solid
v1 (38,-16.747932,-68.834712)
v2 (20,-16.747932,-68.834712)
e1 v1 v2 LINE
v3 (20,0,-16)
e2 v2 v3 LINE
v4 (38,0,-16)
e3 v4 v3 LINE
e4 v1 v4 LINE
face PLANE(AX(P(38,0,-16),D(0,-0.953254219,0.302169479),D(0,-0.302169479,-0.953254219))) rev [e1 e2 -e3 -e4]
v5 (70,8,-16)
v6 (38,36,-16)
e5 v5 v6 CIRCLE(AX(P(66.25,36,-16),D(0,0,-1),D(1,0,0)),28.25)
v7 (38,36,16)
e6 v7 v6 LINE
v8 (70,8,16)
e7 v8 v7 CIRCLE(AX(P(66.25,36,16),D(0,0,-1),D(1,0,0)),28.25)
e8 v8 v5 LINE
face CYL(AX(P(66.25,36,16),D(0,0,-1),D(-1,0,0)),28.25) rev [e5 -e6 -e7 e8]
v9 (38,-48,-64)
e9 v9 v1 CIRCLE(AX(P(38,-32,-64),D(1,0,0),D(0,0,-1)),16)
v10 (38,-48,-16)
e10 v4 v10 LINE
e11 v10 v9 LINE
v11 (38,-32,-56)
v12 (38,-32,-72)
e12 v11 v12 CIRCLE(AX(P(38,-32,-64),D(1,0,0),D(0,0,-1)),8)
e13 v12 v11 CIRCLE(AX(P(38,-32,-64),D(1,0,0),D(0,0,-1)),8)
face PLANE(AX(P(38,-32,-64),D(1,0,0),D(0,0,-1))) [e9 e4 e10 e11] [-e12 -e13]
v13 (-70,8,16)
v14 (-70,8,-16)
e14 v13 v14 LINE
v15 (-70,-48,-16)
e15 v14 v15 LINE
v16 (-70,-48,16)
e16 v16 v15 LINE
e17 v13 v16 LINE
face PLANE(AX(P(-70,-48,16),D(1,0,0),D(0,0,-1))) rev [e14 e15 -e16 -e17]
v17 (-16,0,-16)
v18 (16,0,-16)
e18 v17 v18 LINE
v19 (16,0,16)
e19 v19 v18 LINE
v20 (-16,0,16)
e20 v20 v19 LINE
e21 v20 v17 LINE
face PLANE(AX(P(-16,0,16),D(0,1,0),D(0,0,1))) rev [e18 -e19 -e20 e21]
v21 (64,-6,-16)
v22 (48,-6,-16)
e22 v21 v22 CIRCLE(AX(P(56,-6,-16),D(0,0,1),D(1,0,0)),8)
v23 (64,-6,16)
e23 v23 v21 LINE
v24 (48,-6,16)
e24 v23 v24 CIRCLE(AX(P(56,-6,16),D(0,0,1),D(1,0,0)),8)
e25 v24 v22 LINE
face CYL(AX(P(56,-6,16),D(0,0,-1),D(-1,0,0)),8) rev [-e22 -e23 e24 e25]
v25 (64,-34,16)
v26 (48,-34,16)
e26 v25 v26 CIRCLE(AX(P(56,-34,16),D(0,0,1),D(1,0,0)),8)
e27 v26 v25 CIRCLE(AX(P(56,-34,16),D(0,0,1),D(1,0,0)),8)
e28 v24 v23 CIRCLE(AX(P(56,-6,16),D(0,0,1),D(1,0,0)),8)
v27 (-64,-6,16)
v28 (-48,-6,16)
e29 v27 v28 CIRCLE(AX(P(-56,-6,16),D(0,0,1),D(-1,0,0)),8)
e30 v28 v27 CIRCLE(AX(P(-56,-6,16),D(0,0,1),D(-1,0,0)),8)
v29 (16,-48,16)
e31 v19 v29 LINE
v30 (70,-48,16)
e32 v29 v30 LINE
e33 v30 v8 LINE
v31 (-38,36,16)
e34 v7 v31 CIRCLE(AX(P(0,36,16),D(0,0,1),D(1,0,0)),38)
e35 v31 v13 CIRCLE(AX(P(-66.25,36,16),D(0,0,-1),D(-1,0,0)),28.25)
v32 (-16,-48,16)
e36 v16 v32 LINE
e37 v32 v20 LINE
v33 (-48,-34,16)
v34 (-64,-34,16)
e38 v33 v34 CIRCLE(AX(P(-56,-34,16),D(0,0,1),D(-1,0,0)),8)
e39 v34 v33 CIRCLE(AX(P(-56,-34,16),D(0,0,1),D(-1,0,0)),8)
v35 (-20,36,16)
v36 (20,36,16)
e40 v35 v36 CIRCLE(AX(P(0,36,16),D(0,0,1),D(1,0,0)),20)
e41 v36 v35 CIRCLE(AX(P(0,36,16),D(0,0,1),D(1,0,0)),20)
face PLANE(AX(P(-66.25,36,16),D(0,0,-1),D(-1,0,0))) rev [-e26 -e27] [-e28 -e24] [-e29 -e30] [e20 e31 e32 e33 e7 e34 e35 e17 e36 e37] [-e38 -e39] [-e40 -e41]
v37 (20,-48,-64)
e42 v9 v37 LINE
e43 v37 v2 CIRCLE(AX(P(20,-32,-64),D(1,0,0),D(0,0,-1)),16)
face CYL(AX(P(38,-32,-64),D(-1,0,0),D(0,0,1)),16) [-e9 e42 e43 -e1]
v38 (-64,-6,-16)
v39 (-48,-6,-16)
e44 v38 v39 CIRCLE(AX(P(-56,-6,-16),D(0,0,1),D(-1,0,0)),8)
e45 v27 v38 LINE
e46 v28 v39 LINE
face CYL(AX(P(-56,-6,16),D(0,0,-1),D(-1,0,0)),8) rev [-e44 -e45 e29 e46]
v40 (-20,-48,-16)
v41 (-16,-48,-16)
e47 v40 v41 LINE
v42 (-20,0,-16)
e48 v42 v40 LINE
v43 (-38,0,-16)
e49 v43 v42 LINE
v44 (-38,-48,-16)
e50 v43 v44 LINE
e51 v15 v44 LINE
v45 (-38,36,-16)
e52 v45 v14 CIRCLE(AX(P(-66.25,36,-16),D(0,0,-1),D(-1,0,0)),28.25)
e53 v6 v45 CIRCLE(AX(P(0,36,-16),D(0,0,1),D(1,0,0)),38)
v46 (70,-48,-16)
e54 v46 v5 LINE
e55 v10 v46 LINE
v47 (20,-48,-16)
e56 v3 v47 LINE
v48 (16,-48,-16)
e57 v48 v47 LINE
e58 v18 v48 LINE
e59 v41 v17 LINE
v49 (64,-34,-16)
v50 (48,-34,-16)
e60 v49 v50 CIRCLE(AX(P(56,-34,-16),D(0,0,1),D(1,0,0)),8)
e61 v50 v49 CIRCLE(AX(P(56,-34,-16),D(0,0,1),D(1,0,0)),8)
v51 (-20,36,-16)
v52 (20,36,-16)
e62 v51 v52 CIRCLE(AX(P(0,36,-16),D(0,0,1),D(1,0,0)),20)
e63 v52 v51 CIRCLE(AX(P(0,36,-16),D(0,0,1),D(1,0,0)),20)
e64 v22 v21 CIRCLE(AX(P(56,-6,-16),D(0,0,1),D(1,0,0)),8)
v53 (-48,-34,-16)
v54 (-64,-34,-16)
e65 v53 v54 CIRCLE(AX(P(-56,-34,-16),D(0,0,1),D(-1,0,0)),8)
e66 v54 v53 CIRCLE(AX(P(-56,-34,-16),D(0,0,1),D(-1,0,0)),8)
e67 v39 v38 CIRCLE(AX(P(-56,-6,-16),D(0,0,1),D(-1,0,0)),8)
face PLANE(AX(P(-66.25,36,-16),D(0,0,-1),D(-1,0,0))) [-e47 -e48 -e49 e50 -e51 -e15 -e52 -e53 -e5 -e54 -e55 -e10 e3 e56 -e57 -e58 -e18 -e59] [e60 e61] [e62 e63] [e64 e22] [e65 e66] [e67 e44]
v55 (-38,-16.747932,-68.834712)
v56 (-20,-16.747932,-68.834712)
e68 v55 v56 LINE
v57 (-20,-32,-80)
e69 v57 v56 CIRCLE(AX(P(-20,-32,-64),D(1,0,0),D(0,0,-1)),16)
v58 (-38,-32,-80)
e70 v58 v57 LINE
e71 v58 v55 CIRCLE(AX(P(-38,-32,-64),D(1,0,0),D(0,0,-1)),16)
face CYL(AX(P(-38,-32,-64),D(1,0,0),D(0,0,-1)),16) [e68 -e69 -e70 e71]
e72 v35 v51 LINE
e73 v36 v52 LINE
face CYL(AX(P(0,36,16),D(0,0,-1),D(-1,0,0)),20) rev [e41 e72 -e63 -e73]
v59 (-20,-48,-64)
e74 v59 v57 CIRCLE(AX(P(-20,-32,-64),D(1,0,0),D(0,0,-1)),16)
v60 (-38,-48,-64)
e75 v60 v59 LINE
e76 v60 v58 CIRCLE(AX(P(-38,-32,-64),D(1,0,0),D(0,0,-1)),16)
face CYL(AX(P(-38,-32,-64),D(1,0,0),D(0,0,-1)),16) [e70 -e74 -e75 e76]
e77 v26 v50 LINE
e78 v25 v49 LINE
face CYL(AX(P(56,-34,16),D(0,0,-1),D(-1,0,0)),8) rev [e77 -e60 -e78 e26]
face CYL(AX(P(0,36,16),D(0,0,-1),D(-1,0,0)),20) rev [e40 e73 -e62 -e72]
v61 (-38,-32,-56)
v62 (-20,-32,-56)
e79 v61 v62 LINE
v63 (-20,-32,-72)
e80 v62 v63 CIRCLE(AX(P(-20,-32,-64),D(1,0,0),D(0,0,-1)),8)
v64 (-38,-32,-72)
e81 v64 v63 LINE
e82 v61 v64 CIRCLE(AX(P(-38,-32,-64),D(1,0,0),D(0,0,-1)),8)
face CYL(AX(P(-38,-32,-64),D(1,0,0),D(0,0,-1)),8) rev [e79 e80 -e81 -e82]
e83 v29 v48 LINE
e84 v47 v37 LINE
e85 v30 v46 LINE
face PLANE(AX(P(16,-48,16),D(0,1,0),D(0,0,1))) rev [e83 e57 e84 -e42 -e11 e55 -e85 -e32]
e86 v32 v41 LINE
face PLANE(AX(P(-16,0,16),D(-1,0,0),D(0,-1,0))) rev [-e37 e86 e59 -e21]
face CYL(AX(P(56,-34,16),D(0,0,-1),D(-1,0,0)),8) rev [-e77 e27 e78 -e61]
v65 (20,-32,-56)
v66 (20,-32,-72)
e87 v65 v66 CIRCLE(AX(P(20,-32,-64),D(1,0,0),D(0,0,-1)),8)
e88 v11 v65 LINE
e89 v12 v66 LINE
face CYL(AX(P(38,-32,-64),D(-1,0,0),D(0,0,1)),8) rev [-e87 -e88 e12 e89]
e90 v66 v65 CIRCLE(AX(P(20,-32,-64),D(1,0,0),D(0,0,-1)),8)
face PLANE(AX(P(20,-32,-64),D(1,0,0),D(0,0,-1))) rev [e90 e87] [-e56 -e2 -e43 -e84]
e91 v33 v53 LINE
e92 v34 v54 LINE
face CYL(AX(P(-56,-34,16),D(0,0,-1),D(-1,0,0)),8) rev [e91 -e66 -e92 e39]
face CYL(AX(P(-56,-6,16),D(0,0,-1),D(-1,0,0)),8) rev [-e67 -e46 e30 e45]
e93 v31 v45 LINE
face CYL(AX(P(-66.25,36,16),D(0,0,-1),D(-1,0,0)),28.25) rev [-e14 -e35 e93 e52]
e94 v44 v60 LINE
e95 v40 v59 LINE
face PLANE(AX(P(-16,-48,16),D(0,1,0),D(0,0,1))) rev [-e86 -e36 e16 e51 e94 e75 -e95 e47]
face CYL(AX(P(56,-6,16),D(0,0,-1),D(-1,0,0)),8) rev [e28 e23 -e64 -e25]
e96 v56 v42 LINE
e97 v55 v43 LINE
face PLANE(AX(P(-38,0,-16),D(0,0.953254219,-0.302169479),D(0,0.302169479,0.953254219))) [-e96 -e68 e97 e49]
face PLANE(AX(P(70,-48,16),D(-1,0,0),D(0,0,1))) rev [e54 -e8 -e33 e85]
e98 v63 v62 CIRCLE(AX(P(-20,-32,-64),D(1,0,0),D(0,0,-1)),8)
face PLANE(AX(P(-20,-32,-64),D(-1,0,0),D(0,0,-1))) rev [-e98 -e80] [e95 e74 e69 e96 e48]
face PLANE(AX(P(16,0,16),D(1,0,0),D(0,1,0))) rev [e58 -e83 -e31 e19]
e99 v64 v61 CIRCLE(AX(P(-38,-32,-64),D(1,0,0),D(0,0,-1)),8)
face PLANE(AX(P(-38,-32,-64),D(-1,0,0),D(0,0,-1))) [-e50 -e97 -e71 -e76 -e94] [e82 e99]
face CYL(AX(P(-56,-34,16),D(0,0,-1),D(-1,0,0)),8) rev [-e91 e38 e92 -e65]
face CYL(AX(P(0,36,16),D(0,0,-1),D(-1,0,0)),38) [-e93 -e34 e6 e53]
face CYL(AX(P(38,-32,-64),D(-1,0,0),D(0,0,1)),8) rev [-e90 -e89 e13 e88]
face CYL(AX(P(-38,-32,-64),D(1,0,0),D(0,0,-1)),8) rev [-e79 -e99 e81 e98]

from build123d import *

# Parameters (mm, degrees)
BRACKET_BODY_PROFILE_R   = 20
BRACKET_BODY_PROFILE_R_2 = 8
BRACKET_BODY_32MM_DEPTH  = 16
CLEVIS_LUG_PROFILE_R     = 8
CLEVIS_LUG_18MM_DEPTH    = 18


with BuildPart() as part:
    # Bracket Body Profile → Bracket Body 32mm (new, symmetric)
    with BuildSketch(Plane.XY):
        with BuildLine():
            Line((-16, 0), (16, 0))
            Line((16, 0), (16, -48))
            Line((16, -48), (70, -48))
            Line((70, -48), (70, 8))
            ThreePointArc((70, 8), (47.647244828, 14.739708375), (38, 36))
            ThreePointArc((38, 36), (0, 74), (-38, 36))
            ThreePointArc((-38, 36), (-47.647244828, 14.739708375), (-70, 8))
            Line((-70, 8), (-70, -48))
            Line((-70, -48), (-16, -48))
            Line((-16, -48), (-16, 0))
        make_face()
        with Locations((0, 36)):
            Circle(BRACKET_BODY_PROFILE_R, mode=Mode.SUBTRACT)
        with Locations((56, -34)):
            Circle(BRACKET_BODY_PROFILE_R_2, mode=Mode.SUBTRACT)
        with Locations((56, -6)):
            Circle(BRACKET_BODY_PROFILE_R_2, mode=Mode.SUBTRACT)
        with Locations(Location((-56, -34, 0), (0, 0, 180))):
            Circle(BRACKET_BODY_PROFILE_R_2, mode=Mode.SUBTRACT)
        with Locations(Location((-56, -6, 0), (0, 0, 180))):
            Circle(BRACKET_BODY_PROFILE_R_2, mode=Mode.SUBTRACT)
    extrude(amount=BRACKET_BODY_32MM_DEPTH, both=True)

    # Clevis Lug Profile → Clevis Lug 18mm (add)
    with BuildSketch(Plane(origin=(20, 0, 0), x_dir=(0, 0, -1), z_dir=(1, 0, 0))):
        with BuildLine():
            Line((16, -48), (64, -48))
            ThreePointArc((64, -48), (79.811911333, -34.446111196), (68.834711668, -16.747932498))
            Line((68.834711668, -16.747932498), (16, 0))
            Line((16, 0), (16, -48))
        make_face()
        with Locations((64, -32)):
            Circle(CLEVIS_LUG_PROFILE_R, mode=Mode.SUBTRACT)
    clevis_lug_18mm = extrude(amount=CLEVIS_LUG_18MM_DEPTH)

    # Clevis Lug Mirror: Clevis Lug 18mm across plane
    add(clevis_lug_18mm.mirror(Plane(origin=(0, 0, 0), x_dir=(0, 0, 1), z_dir=(1, 0, 0))))


solid = part.part
